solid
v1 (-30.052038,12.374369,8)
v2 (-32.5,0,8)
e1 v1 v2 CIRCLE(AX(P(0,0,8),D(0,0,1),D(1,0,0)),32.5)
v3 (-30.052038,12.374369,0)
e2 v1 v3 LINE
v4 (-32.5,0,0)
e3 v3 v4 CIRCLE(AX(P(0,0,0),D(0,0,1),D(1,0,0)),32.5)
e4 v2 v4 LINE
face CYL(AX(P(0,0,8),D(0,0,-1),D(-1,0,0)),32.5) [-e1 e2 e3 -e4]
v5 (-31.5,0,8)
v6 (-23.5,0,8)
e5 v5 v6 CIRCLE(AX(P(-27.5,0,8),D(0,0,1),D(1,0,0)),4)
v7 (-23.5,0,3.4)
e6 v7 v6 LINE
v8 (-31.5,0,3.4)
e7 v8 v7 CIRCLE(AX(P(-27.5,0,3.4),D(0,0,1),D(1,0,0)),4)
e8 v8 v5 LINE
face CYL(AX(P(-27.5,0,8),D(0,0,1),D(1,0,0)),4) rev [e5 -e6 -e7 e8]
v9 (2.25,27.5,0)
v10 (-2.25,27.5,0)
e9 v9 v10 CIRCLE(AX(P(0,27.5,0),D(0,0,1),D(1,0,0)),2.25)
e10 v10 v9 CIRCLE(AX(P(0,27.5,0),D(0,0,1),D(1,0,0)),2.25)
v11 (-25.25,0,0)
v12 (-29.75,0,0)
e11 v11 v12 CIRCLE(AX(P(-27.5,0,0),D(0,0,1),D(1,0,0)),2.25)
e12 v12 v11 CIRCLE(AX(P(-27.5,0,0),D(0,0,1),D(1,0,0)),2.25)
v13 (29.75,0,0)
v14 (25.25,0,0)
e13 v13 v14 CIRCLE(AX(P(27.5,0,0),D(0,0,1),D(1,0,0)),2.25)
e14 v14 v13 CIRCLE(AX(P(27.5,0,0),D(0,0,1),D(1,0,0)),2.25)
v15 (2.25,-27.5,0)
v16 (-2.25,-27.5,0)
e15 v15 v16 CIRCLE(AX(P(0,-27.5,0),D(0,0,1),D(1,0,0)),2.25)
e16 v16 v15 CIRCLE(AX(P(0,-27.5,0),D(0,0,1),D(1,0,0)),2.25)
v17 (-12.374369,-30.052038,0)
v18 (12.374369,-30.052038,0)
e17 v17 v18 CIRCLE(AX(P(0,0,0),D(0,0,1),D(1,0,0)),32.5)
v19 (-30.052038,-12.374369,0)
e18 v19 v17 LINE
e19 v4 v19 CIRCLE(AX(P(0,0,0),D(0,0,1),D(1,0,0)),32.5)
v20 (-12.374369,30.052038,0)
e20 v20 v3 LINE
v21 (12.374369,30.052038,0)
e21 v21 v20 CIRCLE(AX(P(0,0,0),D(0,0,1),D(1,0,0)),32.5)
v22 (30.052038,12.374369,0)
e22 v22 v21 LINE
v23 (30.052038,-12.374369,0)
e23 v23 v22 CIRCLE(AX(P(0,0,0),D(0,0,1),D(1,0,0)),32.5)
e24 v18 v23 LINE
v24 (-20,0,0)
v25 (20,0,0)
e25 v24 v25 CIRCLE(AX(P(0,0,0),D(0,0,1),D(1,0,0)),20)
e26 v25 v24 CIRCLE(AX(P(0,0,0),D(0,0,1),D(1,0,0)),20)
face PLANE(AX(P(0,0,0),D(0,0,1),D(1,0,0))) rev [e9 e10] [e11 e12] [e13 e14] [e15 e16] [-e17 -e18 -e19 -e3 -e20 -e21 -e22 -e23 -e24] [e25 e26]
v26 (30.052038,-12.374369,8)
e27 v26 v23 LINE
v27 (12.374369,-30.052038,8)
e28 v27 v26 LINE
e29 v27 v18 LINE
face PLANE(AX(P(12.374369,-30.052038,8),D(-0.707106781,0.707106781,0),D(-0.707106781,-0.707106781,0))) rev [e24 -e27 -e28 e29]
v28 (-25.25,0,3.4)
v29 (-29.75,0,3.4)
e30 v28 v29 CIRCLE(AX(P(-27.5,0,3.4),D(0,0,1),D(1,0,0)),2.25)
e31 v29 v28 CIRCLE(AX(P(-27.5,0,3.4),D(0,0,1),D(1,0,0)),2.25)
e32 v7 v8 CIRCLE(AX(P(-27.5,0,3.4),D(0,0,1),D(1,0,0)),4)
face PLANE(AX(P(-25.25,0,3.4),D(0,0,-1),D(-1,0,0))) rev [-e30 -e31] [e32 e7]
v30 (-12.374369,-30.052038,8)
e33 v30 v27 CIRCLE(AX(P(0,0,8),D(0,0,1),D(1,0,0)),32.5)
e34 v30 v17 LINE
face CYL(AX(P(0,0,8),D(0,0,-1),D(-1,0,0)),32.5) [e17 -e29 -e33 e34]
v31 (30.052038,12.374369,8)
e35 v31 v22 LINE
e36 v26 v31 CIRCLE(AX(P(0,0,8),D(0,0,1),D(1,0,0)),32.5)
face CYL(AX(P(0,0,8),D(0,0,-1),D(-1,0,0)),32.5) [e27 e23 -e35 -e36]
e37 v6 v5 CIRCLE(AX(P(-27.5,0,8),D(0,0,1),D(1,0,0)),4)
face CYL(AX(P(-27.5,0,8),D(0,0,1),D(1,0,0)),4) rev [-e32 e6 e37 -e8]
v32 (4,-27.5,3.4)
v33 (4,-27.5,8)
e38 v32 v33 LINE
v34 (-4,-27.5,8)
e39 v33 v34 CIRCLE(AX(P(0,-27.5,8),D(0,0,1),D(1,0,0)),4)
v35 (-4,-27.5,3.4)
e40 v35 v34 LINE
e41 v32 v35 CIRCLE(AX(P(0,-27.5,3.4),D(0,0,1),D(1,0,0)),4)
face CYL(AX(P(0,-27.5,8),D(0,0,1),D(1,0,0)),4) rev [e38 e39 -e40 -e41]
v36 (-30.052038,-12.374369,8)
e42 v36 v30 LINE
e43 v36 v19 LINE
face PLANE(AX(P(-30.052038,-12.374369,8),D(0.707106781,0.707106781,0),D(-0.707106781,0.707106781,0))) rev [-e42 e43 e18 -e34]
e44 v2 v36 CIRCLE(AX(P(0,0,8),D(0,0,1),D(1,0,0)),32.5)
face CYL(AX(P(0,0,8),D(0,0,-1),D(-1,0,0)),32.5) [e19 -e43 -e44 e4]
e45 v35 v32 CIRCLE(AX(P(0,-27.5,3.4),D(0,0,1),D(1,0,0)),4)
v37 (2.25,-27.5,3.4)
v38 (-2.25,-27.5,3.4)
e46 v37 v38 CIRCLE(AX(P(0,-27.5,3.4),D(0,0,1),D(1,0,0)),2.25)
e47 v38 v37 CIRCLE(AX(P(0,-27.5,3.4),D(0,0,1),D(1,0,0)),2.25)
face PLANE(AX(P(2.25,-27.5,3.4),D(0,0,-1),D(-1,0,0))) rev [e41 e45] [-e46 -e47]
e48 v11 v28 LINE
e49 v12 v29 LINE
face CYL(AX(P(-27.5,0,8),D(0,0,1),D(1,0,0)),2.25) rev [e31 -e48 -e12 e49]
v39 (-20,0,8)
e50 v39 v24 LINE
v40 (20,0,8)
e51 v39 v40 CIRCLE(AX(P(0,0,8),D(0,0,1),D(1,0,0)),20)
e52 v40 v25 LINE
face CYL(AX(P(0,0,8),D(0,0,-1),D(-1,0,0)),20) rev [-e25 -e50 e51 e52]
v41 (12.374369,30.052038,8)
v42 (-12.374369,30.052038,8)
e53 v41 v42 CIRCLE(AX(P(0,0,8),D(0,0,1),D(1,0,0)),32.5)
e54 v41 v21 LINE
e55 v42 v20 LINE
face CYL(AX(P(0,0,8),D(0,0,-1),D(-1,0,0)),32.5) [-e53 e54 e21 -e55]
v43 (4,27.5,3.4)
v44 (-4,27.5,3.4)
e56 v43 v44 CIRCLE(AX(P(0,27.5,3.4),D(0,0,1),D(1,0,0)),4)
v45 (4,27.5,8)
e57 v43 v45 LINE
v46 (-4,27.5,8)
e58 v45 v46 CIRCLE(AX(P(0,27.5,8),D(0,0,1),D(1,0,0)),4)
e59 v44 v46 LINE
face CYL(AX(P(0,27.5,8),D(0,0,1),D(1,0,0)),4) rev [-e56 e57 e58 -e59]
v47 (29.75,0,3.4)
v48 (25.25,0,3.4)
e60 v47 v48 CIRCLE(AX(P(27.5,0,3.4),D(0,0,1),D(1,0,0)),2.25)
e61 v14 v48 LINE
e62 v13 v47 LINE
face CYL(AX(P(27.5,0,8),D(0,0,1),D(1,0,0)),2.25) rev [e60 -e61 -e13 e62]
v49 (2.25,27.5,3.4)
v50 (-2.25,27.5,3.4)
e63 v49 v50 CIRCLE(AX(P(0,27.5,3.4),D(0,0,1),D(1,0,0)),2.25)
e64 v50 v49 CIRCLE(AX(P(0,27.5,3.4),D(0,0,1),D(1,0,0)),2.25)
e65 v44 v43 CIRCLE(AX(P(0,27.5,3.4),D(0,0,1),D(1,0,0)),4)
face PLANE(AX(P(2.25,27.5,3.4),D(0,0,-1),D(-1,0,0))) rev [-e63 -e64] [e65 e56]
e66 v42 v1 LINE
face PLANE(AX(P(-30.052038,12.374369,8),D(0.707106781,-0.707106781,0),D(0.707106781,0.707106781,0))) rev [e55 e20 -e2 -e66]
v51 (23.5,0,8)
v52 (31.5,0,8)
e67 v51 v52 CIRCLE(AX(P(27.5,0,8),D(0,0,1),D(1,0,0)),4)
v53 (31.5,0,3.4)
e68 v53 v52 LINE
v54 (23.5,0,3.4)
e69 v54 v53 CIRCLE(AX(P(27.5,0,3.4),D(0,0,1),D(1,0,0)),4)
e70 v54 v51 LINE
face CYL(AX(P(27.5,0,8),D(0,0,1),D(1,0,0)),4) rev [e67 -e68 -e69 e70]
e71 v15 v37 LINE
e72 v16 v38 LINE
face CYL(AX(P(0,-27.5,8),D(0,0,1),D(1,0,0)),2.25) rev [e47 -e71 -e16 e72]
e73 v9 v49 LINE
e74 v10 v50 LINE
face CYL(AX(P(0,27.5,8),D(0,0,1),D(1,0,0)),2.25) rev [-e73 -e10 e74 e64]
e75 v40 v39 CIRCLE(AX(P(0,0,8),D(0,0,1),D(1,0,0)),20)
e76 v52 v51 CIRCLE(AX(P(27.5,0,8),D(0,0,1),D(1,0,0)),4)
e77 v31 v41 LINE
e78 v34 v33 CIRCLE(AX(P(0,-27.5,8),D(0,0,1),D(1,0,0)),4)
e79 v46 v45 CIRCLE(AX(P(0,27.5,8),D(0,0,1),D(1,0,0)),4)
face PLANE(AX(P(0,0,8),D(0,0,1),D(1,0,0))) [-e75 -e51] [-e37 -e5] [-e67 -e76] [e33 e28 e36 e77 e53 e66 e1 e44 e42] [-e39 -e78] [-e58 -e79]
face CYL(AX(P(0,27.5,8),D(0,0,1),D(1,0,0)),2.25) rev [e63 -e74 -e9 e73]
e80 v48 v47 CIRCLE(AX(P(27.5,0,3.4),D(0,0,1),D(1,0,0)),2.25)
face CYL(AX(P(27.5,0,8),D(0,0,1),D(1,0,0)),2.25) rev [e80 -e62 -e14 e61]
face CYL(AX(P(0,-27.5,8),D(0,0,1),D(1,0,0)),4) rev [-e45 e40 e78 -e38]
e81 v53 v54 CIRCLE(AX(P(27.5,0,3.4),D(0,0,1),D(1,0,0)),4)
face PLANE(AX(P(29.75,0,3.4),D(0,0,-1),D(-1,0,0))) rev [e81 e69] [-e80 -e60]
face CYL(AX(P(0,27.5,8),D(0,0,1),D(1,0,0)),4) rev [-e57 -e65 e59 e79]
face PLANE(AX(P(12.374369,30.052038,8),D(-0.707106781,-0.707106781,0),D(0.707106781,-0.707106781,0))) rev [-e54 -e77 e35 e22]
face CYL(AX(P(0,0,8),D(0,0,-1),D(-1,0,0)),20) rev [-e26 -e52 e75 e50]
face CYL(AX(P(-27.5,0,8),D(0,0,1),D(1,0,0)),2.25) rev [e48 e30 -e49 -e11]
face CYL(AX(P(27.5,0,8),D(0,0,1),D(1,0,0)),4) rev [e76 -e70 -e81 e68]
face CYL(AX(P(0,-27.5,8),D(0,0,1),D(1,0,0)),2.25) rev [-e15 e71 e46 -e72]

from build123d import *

# Parameters (mm, degrees)
SKETCH1_R                                            = 20
BOSS_EXTRUDE1_DEPTH                                  = 8
HOLE_SIZE_PER_SOCKET_HEAD_CAP_SCREW_TYPE_D           = 4.5
HOLE_SIZE_PER_SOCKET_HEAD_CAP_SCREW_TYPE_CBORE_D     = 8
HOLE_SIZE_PER_SOCKET_HEAD_CAP_SCREW_TYPE_CBORE_DEPTH = 4.6


with BuildPart() as part:
    # Sketch1 → Boss-Extrude1 (new body)
    with BuildSketch(Plane.XY):
        with BuildLine():
            Line((-30.0520382, -12.374368671), (-12.374368671, -30.0520382))
            ThreePointArc((-12.374368671, -30.0520382), (0, -32.5), (12.374368671, -30.0520382))
            Line((12.374368671, -30.0520382), (30.0520382, -12.374368671))
            ThreePointArc((30.0520382, -12.374368671), (32.5, 0), (30.0520382, 12.374368671))
            Line((30.0520382, 12.374368671), (12.374368671, 30.0520382))
            ThreePointArc((12.374368671, 30.0520382), (0, 32.5), (-12.374368671, 30.0520382))
            Line((-12.374368671, 30.0520382), (-30.0520382, 12.374368671))
            ThreePointArc((-30.0520382, 12.374368671), (-32.5, 0), (-30.0520382, -12.374368671))
        make_face()
        Circle(SKETCH1_R, mode=Mode.SUBTRACT)
    extrude(amount=BOSS_EXTRUDE1_DEPTH)

    # Hole size per socket head cap screw type 1 (through all)
    with Locations(Plane.XY.offset(8)):
        with Locations((0, 27.5), (-27.5, 0), (0, -27.5), (27.5, 0)):
            CounterBoreHole(HOLE_SIZE_PER_SOCKET_HEAD_CAP_SCREW_TYPE_D / 2, HOLE_SIZE_PER_SOCKET_HEAD_CAP_SCREW_TYPE_CBORE_D / 2, HOLE_SIZE_PER_SOCKET_HEAD_CAP_SCREW_TYPE_CBORE_DEPTH)


solid = part.part
